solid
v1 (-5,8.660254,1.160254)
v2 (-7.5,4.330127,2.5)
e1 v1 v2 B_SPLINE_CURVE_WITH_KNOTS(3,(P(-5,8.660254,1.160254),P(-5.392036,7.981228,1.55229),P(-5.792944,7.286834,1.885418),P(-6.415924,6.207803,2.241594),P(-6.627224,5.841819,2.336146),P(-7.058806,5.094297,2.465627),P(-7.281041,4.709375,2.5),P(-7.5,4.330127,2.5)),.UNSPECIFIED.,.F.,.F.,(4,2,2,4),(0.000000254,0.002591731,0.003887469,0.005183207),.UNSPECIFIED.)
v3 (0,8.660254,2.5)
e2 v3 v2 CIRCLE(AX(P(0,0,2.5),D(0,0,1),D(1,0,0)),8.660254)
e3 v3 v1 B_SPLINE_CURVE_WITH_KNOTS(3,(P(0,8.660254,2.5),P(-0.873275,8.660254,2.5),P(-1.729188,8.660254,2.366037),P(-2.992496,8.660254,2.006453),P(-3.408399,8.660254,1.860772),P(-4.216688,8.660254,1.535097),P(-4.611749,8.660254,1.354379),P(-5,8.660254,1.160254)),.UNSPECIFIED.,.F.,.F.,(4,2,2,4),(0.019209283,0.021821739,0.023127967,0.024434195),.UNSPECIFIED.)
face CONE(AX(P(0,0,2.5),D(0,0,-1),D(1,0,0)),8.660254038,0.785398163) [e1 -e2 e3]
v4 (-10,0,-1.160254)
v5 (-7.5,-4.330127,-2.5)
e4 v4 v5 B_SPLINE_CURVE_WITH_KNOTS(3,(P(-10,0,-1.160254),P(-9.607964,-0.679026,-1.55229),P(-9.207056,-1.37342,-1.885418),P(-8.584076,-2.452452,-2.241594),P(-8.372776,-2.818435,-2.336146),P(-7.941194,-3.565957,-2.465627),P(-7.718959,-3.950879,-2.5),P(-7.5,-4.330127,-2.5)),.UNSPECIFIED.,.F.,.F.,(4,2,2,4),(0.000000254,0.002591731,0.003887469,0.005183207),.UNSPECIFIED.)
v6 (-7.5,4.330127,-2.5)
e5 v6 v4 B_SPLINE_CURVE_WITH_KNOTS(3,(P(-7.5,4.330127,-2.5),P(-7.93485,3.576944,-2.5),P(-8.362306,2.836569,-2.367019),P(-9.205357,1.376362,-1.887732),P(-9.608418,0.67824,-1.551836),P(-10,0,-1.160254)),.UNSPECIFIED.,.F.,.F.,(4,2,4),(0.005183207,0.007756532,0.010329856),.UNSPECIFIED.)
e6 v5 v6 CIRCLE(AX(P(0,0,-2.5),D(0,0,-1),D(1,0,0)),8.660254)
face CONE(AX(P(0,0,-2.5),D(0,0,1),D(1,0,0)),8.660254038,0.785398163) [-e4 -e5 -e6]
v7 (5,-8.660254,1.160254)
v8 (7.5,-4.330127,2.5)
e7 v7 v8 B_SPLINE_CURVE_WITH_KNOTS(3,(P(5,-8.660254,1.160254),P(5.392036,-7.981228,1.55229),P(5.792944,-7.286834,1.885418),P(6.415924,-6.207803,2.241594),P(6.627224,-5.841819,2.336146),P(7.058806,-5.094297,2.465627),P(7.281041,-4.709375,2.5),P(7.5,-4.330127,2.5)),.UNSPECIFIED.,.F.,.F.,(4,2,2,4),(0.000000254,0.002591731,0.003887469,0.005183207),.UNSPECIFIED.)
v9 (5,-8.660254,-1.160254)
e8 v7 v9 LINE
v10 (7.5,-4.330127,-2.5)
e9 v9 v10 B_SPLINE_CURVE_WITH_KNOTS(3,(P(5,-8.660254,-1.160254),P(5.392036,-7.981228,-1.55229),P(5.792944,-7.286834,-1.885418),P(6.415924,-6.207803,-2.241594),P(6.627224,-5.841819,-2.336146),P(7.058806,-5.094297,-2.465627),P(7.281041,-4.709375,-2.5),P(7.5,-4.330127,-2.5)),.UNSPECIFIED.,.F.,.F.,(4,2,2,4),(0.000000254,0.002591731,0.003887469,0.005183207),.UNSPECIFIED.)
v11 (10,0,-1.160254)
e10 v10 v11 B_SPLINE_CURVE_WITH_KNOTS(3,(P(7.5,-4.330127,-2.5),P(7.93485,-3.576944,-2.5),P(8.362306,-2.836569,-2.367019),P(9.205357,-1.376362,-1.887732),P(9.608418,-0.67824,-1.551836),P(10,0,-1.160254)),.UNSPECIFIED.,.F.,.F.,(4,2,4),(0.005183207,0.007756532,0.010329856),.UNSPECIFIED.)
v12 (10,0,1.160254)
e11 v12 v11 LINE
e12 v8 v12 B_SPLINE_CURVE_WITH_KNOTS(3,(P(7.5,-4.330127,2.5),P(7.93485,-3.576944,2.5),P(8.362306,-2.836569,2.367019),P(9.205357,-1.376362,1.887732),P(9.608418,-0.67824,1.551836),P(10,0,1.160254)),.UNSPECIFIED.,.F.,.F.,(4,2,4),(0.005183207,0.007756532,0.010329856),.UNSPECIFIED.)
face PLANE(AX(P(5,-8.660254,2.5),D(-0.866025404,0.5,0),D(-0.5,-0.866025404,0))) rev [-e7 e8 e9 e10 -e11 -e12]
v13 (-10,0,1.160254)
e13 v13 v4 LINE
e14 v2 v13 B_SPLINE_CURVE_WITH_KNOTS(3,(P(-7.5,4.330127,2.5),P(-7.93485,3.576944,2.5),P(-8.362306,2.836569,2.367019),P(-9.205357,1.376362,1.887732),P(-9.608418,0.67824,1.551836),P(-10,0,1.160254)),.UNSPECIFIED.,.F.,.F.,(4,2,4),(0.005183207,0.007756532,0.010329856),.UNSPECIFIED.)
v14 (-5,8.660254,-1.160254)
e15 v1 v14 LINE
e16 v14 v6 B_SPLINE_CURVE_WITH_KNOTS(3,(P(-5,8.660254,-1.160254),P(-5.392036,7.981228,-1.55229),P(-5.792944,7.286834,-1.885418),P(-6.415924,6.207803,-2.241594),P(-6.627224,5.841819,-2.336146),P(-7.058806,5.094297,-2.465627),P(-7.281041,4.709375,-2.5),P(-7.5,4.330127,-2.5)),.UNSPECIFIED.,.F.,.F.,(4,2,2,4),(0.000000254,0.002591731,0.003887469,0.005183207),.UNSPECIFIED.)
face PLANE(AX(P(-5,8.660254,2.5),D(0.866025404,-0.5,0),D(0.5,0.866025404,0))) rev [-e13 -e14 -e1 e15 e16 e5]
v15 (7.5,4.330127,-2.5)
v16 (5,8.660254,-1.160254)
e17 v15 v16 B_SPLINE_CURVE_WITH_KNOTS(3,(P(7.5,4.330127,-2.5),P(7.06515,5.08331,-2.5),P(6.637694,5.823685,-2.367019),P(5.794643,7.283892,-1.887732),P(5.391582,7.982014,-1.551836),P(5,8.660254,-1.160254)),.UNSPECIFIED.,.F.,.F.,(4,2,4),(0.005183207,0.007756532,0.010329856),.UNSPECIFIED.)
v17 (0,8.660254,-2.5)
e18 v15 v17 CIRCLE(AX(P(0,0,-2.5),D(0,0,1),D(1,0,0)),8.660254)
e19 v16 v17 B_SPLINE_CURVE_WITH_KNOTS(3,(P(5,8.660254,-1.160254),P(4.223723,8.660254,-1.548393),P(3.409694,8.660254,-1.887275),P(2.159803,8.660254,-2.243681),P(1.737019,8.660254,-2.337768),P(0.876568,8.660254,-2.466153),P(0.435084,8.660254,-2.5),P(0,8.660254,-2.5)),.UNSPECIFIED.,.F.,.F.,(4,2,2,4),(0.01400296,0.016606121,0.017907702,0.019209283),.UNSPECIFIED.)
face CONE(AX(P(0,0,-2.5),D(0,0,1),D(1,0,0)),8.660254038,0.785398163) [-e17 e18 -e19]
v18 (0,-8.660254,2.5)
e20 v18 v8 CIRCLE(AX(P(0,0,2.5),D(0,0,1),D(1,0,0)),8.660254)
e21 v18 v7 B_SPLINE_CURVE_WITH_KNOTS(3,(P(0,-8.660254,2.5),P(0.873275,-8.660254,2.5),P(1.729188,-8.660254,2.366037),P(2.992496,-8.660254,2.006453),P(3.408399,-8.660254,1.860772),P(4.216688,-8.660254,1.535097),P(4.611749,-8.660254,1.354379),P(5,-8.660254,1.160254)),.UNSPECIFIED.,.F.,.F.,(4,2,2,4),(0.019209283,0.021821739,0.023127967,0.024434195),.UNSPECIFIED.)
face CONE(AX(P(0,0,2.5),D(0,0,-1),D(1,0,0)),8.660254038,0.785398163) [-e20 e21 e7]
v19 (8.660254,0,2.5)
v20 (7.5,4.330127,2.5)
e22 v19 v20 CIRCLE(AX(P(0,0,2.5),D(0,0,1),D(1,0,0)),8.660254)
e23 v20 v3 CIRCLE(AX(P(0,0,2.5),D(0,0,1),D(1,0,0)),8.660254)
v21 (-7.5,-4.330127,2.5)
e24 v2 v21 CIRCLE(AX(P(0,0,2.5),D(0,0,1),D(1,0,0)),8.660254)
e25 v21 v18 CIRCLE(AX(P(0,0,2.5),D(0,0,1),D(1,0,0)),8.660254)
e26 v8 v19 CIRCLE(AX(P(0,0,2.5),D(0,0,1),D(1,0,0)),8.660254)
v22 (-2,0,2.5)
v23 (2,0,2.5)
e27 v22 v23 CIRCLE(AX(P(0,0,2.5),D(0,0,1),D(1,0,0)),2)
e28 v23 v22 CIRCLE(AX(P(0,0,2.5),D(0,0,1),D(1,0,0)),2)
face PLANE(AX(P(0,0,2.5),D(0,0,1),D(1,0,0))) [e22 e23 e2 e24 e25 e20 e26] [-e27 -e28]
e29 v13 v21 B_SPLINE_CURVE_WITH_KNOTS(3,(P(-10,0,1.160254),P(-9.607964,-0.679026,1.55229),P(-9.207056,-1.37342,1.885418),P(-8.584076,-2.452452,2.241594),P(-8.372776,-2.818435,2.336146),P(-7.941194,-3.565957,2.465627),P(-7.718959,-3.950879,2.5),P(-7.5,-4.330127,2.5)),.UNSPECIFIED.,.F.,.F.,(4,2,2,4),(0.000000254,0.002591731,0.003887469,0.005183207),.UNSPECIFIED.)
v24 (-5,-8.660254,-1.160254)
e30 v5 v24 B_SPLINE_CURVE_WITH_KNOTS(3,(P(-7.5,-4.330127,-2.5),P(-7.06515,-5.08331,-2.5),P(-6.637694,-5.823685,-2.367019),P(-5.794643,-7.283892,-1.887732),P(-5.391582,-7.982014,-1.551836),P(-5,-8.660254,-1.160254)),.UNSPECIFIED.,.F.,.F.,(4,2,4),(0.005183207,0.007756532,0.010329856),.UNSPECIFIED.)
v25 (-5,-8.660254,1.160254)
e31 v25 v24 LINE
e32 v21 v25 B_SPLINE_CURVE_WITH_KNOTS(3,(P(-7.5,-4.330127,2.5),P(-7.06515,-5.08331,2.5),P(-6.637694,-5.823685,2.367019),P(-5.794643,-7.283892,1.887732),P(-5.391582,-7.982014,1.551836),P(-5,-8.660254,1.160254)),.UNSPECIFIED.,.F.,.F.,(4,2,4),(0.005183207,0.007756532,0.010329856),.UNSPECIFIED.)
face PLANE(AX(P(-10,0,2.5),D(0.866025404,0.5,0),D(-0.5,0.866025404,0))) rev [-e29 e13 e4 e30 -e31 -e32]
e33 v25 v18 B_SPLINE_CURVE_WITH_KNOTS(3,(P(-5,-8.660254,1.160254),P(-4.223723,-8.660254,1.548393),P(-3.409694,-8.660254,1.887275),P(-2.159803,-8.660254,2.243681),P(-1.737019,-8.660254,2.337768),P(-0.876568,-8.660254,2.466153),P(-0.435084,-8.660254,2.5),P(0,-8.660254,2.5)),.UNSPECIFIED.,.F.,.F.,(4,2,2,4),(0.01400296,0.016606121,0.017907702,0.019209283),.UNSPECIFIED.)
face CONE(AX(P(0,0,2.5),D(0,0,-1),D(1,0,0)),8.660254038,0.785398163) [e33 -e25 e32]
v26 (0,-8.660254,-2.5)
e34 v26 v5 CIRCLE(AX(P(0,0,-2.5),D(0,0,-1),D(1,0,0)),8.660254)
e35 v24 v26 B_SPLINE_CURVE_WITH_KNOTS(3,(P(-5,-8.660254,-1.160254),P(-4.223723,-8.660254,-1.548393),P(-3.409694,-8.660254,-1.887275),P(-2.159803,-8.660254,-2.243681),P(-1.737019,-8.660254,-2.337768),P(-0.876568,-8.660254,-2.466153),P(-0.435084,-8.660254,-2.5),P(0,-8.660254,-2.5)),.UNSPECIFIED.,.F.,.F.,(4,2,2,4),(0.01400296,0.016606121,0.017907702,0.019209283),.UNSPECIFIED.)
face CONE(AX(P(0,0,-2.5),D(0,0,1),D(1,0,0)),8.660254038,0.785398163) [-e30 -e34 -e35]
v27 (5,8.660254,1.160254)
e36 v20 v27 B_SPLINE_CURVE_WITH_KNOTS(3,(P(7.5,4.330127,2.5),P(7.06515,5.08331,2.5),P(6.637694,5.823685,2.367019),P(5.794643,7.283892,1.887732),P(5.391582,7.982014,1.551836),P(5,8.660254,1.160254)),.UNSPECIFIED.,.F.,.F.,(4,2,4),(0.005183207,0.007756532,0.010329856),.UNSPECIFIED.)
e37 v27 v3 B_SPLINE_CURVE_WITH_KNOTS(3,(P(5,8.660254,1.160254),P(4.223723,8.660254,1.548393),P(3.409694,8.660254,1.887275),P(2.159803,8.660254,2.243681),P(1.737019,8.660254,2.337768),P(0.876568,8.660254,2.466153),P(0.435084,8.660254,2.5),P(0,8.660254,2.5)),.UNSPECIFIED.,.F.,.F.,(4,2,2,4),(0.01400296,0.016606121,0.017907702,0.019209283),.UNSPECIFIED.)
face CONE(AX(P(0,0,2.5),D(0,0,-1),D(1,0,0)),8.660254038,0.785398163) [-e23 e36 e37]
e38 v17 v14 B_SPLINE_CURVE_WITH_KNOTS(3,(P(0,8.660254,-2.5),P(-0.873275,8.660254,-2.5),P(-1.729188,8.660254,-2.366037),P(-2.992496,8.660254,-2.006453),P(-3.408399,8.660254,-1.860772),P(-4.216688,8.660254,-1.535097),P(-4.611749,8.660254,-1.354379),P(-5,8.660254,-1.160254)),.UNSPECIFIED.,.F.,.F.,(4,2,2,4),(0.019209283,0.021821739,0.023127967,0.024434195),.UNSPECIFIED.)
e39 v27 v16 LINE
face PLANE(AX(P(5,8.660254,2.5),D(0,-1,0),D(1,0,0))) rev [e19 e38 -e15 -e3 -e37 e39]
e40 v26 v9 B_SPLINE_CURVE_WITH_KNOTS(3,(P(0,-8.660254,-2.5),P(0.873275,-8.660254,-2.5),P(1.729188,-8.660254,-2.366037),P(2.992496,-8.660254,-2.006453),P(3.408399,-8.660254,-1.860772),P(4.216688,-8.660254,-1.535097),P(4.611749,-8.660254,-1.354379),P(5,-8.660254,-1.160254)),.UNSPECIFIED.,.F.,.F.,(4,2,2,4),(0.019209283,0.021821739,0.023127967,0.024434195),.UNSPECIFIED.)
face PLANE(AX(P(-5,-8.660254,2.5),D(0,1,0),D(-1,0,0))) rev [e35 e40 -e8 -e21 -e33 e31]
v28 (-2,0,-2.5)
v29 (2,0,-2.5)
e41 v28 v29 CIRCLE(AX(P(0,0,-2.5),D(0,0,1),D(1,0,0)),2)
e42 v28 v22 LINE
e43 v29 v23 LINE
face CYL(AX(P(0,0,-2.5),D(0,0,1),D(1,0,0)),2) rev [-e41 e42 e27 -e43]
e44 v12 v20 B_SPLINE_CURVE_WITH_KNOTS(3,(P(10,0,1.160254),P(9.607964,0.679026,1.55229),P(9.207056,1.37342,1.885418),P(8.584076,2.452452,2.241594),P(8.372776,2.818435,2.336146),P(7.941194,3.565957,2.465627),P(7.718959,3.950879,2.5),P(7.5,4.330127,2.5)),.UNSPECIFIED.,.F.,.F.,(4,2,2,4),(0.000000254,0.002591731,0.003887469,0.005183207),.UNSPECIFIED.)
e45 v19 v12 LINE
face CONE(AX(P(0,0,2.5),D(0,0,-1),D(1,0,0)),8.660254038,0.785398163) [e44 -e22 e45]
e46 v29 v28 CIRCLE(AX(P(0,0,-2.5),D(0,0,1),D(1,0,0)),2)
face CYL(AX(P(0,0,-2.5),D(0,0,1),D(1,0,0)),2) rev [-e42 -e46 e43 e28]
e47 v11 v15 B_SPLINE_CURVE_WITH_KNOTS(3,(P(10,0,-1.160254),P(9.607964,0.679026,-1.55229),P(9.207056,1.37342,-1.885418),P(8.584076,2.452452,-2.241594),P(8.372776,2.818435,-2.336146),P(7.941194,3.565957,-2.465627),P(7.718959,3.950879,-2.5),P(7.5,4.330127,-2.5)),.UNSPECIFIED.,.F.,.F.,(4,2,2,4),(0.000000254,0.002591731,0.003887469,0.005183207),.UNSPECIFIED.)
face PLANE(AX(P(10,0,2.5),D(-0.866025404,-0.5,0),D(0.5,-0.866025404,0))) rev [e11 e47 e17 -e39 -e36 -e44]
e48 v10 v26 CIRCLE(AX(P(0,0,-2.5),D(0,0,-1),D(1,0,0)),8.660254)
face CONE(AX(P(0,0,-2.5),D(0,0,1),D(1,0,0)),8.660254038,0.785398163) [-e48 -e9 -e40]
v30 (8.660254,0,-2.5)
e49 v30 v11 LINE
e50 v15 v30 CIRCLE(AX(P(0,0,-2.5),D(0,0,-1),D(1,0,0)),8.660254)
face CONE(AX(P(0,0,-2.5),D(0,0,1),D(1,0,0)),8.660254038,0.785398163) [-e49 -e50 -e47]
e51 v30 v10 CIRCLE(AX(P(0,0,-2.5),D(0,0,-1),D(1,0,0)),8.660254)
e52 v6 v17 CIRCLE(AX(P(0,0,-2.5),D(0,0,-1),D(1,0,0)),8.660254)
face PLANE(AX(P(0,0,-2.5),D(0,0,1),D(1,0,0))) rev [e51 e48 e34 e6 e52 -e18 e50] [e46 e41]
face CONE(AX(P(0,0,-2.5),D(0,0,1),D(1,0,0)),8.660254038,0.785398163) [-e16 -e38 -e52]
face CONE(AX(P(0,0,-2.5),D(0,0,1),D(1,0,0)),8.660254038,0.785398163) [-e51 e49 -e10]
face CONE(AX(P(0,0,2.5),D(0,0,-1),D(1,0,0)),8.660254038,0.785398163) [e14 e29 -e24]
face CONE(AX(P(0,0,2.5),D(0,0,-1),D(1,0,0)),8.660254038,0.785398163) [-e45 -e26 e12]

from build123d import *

# Parameters (mm, degrees)
HEX_BODY_DEPTH                        = 2.5
BORE_SKETCH_R                         = 2
BORE_4_DEPTH                          = 15.142135624
CORNER_CHAMFER_SKETCH_OUTSIDE_W       = 37.386
CORNER_CHAMFER_SKETCH_OUTSIDE_H       = 34.706
CORNER_CHAMFER_SKETCH_OUTSIDE_R       = 8.660254038
CORNER_CHAMFER_45DEG_DEPTH            = 5
CORNER_CHAMFER_45DEG_DRAFT            = -45
CORNER_CHAMFER_MIRROR_COPY_1_SKETCH_W = 37.386
CORNER_CHAMFER_MIRROR_COPY_1_SKETCH_H = 34.706
CORNER_CHAMFER_MIRROR_COPY_1_SKETCH_R = 8.660254038
CORNER_CHAMFER_MIRROR_COPY_1_DEPTH    = 5
CORNER_CHAMFER_MIRROR_COPY_1_DRAFT    = -45


with BuildPart() as part:
    # Hex Profile Sketch → Hex Body (new, symmetric)
    with BuildSketch(Plane.XY):
        Polygon((10, 0), (5, 8.660254038), (-5, 8.660254038), (-10, 0), (-5, -8.660254038), (5, -8.660254038), align=None)
    extrude(amount=HEX_BODY_DEPTH, both=True)

    # Bore Sketch → Bore Ø4 (cut, through all)
    with BuildSketch(Plane.XY.offset(2.5)):
        Circle(BORE_SKETCH_R)
    extrude(amount=-BORE_4_DEPTH, mode=Mode.SUBTRACT)


with BuildPart() as corner_chamfer_45deg_tool:
    # Corner Chamfer Sketch outside → Corner Chamfer 45deg (with draft: the straight prism first)
    with BuildSketch(Plane.XY.offset(2.5)):
        Rectangle(CORNER_CHAMFER_SKETCH_OUTSIDE_W, CORNER_CHAMFER_SKETCH_OUTSIDE_H)
        Circle(CORNER_CHAMFER_SKETCH_OUTSIDE_R, mode=Mode.SUBTRACT)
    extrude(amount=-CORNER_CHAMFER_45DEG_DEPTH)
    # Corner Chamfer 45deg: the draft: its side faces are tilted about the plane it starts from
    corner_chamfer_45deg_sides = [corner_chamfer_45deg_tool.faces().sort_by_distance(p)[0] for p in [
        (0, -17.353, 0),
        (18.693, 0, 0),
        (0, 17.353, 0),
        (-18.693, 0, 0),
        (-8.660254038, 0, 0),
    ]]
    draft(corner_chamfer_45deg_sides, Plane.XY.offset(2.5), CORNER_CHAMFER_45DEG_DRAFT)


with BuildPart() as part_1:
    add(part.part)

    # Corner Chamfer 45deg: cut by corner_chamfer_45deg_tool
    add(corner_chamfer_45deg_tool.part, mode=Mode.SUBTRACT)


with BuildPart() as corner_chamfer_mirror_copy_1_tool:
    # Corner Chamfer Mirror copy 1 sketch → Corner Chamfer Mirror copy 1 (with draft: the straight prism first)
    with BuildSketch(Plane(origin=(0, 0, -2.5), x_dir=(1, 0, 0), z_dir=(0, 0, -1))):
        Rectangle(CORNER_CHAMFER_MIRROR_COPY_1_SKETCH_W, CORNER_CHAMFER_MIRROR_COPY_1_SKETCH_H)
        Circle(CORNER_CHAMFER_MIRROR_COPY_1_SKETCH_R, mode=Mode.SUBTRACT)
    extrude(amount=-CORNER_CHAMFER_MIRROR_COPY_1_DEPTH)
    # Corner Chamfer Mirror copy 1: the draft: its side faces are tilted about the plane it starts from
    corner_chamfer_mirror_copy_1_sides = [corner_chamfer_mirror_copy_1_tool.faces().sort_by_distance(p)[0] for p in [
        (0, -17.353, 0),
        (18.693, 0, 0),
        (0, 17.353, 0),
        (-18.693, 0, 0),
        (-8.660254038, 0, 0),
    ]]
    draft(corner_chamfer_mirror_copy_1_sides, Plane(origin=(0, 0, -2.5), x_dir=(1, 0, 0), z_dir=(0, 0, -1)), CORNER_CHAMFER_MIRROR_COPY_1_DRAFT)


with BuildPart() as part_2:
    add(part_1.part)

    # Corner Chamfer Mirror copy 1: cut by corner_chamfer_mirror_copy_1_tool
    add(corner_chamfer_mirror_copy_1_tool.part, mode=Mode.SUBTRACT)


solid = part_2.part
